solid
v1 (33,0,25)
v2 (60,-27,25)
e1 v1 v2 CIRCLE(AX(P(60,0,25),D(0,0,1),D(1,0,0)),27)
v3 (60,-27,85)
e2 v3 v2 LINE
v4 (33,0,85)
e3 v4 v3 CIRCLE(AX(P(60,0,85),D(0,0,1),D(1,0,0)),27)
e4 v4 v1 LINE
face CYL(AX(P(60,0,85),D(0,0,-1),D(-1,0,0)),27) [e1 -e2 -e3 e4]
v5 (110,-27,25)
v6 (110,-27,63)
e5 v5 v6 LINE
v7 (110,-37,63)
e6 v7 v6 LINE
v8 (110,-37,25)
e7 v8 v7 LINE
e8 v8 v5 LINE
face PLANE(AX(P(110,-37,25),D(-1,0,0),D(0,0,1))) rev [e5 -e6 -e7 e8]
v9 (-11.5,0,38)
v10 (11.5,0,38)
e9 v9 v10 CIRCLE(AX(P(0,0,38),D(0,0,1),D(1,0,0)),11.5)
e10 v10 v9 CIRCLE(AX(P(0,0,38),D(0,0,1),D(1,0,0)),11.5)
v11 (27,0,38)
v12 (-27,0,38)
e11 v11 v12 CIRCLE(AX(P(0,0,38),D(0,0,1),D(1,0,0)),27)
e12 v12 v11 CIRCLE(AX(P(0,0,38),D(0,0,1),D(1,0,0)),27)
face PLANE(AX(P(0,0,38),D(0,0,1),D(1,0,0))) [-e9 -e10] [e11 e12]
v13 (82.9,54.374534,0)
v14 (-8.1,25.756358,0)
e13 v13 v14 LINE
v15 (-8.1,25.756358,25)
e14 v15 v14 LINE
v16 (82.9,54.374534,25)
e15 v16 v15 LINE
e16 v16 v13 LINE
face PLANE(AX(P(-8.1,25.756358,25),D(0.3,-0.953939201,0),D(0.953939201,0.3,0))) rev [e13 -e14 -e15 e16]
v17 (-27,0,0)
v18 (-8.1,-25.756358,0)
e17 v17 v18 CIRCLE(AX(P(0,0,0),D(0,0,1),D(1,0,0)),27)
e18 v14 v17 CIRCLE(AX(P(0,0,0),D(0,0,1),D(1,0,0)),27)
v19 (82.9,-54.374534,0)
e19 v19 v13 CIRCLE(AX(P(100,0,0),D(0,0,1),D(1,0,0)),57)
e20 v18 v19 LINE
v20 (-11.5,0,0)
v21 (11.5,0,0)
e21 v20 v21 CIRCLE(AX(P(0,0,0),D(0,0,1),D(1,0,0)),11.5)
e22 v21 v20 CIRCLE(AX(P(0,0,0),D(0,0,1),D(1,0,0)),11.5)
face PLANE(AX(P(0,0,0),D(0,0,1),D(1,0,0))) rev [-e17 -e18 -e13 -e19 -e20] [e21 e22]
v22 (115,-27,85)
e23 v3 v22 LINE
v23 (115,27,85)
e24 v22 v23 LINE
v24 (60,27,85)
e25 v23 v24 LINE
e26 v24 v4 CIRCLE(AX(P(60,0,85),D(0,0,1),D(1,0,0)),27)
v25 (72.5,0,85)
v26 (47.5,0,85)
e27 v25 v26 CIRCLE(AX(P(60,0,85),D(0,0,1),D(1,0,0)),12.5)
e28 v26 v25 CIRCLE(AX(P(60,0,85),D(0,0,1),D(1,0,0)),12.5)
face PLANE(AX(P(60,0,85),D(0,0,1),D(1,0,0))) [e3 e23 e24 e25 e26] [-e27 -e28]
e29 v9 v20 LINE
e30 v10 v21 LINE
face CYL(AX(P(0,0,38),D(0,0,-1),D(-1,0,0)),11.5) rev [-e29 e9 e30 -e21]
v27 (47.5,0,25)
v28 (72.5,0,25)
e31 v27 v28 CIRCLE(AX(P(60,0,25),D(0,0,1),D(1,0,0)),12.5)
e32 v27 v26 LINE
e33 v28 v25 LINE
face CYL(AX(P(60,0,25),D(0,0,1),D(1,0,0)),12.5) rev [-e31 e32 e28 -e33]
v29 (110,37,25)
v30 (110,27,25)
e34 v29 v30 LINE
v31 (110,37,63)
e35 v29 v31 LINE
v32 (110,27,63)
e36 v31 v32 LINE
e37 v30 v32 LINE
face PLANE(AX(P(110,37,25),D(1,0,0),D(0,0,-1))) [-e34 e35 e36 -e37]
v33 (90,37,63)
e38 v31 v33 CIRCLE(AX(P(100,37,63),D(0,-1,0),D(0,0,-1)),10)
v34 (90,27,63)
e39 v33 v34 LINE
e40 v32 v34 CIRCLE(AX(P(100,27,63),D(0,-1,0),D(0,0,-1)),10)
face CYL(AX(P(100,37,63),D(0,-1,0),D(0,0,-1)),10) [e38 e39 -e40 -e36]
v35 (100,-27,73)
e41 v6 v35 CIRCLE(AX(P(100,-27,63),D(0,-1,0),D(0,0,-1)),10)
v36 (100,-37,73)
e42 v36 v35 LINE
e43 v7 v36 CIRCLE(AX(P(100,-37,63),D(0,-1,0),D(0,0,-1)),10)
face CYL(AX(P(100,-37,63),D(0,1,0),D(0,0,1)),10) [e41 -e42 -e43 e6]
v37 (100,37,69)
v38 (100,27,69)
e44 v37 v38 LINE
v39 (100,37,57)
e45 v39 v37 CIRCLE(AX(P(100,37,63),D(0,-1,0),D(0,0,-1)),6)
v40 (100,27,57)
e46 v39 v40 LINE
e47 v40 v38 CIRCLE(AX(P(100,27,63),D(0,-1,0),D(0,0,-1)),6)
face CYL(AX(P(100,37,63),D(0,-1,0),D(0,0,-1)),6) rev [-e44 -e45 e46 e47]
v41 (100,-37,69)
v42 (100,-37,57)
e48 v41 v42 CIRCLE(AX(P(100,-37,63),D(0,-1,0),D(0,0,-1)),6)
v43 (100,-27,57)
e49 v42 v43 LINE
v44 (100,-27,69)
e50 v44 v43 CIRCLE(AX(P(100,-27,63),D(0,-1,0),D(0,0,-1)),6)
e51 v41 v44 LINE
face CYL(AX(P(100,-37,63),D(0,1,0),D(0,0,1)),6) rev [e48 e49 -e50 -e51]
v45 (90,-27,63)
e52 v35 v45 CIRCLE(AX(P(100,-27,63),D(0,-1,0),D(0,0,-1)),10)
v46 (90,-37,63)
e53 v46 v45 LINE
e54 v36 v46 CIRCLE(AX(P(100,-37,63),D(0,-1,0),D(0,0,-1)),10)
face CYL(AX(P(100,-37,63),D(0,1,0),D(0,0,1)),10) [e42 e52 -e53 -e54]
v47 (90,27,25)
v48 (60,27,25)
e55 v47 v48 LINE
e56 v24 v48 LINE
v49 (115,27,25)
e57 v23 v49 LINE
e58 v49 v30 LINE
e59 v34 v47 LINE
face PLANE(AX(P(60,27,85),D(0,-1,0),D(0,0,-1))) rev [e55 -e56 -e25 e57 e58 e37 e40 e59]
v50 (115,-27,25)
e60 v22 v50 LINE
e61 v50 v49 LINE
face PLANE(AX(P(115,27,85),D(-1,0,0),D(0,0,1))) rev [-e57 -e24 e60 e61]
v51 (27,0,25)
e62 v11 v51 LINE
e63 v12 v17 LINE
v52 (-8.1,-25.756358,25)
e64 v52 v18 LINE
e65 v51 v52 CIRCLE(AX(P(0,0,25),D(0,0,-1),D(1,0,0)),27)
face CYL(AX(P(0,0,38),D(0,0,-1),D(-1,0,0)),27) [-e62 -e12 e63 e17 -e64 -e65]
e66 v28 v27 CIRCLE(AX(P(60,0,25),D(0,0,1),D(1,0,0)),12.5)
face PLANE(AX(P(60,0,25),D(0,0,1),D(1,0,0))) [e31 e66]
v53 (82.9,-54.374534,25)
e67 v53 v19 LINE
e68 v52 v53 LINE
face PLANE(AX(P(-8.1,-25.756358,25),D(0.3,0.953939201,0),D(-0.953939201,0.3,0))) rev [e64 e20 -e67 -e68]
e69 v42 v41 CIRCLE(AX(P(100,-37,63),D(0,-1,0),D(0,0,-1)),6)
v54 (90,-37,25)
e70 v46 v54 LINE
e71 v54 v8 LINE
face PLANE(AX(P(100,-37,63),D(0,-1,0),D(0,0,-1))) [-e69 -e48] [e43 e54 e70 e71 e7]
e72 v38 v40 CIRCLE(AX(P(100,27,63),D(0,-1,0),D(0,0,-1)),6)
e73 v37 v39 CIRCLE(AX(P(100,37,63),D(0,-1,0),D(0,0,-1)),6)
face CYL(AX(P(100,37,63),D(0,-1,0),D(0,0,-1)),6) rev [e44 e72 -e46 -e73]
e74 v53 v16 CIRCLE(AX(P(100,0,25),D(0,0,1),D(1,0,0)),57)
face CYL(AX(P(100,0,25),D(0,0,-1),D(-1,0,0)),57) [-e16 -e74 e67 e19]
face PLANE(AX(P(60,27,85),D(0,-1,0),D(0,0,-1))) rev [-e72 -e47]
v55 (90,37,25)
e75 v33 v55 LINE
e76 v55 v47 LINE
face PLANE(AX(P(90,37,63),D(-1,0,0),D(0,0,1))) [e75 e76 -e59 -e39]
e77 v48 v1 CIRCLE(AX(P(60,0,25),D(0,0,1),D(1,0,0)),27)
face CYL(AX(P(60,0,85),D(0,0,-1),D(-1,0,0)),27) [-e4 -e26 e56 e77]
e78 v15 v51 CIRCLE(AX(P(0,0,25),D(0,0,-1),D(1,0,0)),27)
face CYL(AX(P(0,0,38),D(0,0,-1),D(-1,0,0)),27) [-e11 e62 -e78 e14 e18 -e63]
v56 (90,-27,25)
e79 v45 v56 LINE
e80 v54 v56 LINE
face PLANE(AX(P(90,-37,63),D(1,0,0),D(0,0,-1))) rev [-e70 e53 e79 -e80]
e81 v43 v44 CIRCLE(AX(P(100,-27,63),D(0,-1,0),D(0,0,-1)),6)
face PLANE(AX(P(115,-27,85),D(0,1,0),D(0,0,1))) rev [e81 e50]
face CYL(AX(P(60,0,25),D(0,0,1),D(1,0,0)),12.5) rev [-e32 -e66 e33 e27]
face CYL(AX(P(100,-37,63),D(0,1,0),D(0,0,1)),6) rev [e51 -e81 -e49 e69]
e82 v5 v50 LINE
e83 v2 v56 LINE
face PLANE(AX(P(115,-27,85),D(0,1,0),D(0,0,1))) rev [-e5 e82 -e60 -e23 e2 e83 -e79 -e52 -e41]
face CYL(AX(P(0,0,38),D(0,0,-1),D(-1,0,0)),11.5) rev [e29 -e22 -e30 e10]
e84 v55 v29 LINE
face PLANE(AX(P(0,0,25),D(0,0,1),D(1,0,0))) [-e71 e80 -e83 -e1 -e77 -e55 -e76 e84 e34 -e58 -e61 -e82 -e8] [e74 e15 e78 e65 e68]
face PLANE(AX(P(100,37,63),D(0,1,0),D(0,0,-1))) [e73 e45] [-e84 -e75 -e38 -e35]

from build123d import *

# Parameters (mm, degrees)
PIVOT_BOSS_SKETCH_R   = 27
PIVOT_BOSS_SKETCH_R_2 = 11.5
PIVOT_BOSS_DEPTH      = 38
MOUNTING_PLATE_DEPTH  = 25
ARM_BLOCK_DEPTH       = 60
PIVOT_BORE_SKETCH_R   = 12.5
PIVOT_BORE_25_DEPTH   = 60
CLAMP_TAB_SKETCH_R    = 6
CLAMP_TAB_DEPTH       = 10


with BuildPart() as part:
    # Pivot Boss Sketch → Pivot Boss (new body)
    with BuildSketch(Plane.XY):
        Circle(PIVOT_BOSS_SKETCH_R)
        Circle(PIVOT_BOSS_SKETCH_R_2, mode=Mode.SUBTRACT)
    extrude(amount=PIVOT_BOSS_DEPTH)

    # Mounting Plate Sketch → Mounting Plate (add)
    with BuildSketch(Plane.XY):
        with BuildLine():
            Line((-8.1, 25.756358438), (82.9, 54.374534481))
            ThreePointArc((82.9, 54.374534481), (157, 0), (82.9, -54.374534481))
            Line((82.9, -54.374534481), (-8.1, -25.756358438))
            ThreePointArc((-8.1, -25.756358438), (27, 0), (-8.1, 25.756358438))
        make_face()
    extrude(amount=MOUNTING_PLATE_DEPTH)

    # Arm Block Sketch → Arm Block (add)
    with BuildSketch(Plane.XY.offset(25)):
        with BuildLine():
            Line((60, 27), (115, 27))
            Line((115, 27), (115, -27))
            Line((115, -27), (60, -27))
            ThreePointArc((60, -27), (33, 0), (60, 27))
        make_face()
    extrude(amount=ARM_BLOCK_DEPTH)

    # Pivot Bore Sketch → Pivot Bore Ø25 (cut)
    with BuildSketch(Plane.XY.offset(85)):
        with Locations((60, 0)):
            Circle(PIVOT_BORE_SKETCH_R)
    extrude(amount=-PIVOT_BORE_25_DEPTH, mode=Mode.SUBTRACT)

    # Clamp Tab Sketch → Clamp Tab (add)
    with BuildSketch(Plane.XZ.offset(27)):
        with BuildLine():
            Line((90, 63), (90, 25))
            Line((90, 25), (110, 25))
            Line((110, 25), (110, 63))
            ThreePointArc((110, 63), (100, 73), (90, 63))
        make_face()
        with Locations(Location((100, 63, 0), (0, 0, 270))):
            Circle(CLAMP_TAB_SKETCH_R, mode=Mode.SUBTRACT)
    clamp_tab = extrude(amount=CLAMP_TAB_DEPTH)

    # Clamp Tab Mirror: Clamp Tab across plane
    add(clamp_tab.mirror(Plane.ZX))


solid = part.part
